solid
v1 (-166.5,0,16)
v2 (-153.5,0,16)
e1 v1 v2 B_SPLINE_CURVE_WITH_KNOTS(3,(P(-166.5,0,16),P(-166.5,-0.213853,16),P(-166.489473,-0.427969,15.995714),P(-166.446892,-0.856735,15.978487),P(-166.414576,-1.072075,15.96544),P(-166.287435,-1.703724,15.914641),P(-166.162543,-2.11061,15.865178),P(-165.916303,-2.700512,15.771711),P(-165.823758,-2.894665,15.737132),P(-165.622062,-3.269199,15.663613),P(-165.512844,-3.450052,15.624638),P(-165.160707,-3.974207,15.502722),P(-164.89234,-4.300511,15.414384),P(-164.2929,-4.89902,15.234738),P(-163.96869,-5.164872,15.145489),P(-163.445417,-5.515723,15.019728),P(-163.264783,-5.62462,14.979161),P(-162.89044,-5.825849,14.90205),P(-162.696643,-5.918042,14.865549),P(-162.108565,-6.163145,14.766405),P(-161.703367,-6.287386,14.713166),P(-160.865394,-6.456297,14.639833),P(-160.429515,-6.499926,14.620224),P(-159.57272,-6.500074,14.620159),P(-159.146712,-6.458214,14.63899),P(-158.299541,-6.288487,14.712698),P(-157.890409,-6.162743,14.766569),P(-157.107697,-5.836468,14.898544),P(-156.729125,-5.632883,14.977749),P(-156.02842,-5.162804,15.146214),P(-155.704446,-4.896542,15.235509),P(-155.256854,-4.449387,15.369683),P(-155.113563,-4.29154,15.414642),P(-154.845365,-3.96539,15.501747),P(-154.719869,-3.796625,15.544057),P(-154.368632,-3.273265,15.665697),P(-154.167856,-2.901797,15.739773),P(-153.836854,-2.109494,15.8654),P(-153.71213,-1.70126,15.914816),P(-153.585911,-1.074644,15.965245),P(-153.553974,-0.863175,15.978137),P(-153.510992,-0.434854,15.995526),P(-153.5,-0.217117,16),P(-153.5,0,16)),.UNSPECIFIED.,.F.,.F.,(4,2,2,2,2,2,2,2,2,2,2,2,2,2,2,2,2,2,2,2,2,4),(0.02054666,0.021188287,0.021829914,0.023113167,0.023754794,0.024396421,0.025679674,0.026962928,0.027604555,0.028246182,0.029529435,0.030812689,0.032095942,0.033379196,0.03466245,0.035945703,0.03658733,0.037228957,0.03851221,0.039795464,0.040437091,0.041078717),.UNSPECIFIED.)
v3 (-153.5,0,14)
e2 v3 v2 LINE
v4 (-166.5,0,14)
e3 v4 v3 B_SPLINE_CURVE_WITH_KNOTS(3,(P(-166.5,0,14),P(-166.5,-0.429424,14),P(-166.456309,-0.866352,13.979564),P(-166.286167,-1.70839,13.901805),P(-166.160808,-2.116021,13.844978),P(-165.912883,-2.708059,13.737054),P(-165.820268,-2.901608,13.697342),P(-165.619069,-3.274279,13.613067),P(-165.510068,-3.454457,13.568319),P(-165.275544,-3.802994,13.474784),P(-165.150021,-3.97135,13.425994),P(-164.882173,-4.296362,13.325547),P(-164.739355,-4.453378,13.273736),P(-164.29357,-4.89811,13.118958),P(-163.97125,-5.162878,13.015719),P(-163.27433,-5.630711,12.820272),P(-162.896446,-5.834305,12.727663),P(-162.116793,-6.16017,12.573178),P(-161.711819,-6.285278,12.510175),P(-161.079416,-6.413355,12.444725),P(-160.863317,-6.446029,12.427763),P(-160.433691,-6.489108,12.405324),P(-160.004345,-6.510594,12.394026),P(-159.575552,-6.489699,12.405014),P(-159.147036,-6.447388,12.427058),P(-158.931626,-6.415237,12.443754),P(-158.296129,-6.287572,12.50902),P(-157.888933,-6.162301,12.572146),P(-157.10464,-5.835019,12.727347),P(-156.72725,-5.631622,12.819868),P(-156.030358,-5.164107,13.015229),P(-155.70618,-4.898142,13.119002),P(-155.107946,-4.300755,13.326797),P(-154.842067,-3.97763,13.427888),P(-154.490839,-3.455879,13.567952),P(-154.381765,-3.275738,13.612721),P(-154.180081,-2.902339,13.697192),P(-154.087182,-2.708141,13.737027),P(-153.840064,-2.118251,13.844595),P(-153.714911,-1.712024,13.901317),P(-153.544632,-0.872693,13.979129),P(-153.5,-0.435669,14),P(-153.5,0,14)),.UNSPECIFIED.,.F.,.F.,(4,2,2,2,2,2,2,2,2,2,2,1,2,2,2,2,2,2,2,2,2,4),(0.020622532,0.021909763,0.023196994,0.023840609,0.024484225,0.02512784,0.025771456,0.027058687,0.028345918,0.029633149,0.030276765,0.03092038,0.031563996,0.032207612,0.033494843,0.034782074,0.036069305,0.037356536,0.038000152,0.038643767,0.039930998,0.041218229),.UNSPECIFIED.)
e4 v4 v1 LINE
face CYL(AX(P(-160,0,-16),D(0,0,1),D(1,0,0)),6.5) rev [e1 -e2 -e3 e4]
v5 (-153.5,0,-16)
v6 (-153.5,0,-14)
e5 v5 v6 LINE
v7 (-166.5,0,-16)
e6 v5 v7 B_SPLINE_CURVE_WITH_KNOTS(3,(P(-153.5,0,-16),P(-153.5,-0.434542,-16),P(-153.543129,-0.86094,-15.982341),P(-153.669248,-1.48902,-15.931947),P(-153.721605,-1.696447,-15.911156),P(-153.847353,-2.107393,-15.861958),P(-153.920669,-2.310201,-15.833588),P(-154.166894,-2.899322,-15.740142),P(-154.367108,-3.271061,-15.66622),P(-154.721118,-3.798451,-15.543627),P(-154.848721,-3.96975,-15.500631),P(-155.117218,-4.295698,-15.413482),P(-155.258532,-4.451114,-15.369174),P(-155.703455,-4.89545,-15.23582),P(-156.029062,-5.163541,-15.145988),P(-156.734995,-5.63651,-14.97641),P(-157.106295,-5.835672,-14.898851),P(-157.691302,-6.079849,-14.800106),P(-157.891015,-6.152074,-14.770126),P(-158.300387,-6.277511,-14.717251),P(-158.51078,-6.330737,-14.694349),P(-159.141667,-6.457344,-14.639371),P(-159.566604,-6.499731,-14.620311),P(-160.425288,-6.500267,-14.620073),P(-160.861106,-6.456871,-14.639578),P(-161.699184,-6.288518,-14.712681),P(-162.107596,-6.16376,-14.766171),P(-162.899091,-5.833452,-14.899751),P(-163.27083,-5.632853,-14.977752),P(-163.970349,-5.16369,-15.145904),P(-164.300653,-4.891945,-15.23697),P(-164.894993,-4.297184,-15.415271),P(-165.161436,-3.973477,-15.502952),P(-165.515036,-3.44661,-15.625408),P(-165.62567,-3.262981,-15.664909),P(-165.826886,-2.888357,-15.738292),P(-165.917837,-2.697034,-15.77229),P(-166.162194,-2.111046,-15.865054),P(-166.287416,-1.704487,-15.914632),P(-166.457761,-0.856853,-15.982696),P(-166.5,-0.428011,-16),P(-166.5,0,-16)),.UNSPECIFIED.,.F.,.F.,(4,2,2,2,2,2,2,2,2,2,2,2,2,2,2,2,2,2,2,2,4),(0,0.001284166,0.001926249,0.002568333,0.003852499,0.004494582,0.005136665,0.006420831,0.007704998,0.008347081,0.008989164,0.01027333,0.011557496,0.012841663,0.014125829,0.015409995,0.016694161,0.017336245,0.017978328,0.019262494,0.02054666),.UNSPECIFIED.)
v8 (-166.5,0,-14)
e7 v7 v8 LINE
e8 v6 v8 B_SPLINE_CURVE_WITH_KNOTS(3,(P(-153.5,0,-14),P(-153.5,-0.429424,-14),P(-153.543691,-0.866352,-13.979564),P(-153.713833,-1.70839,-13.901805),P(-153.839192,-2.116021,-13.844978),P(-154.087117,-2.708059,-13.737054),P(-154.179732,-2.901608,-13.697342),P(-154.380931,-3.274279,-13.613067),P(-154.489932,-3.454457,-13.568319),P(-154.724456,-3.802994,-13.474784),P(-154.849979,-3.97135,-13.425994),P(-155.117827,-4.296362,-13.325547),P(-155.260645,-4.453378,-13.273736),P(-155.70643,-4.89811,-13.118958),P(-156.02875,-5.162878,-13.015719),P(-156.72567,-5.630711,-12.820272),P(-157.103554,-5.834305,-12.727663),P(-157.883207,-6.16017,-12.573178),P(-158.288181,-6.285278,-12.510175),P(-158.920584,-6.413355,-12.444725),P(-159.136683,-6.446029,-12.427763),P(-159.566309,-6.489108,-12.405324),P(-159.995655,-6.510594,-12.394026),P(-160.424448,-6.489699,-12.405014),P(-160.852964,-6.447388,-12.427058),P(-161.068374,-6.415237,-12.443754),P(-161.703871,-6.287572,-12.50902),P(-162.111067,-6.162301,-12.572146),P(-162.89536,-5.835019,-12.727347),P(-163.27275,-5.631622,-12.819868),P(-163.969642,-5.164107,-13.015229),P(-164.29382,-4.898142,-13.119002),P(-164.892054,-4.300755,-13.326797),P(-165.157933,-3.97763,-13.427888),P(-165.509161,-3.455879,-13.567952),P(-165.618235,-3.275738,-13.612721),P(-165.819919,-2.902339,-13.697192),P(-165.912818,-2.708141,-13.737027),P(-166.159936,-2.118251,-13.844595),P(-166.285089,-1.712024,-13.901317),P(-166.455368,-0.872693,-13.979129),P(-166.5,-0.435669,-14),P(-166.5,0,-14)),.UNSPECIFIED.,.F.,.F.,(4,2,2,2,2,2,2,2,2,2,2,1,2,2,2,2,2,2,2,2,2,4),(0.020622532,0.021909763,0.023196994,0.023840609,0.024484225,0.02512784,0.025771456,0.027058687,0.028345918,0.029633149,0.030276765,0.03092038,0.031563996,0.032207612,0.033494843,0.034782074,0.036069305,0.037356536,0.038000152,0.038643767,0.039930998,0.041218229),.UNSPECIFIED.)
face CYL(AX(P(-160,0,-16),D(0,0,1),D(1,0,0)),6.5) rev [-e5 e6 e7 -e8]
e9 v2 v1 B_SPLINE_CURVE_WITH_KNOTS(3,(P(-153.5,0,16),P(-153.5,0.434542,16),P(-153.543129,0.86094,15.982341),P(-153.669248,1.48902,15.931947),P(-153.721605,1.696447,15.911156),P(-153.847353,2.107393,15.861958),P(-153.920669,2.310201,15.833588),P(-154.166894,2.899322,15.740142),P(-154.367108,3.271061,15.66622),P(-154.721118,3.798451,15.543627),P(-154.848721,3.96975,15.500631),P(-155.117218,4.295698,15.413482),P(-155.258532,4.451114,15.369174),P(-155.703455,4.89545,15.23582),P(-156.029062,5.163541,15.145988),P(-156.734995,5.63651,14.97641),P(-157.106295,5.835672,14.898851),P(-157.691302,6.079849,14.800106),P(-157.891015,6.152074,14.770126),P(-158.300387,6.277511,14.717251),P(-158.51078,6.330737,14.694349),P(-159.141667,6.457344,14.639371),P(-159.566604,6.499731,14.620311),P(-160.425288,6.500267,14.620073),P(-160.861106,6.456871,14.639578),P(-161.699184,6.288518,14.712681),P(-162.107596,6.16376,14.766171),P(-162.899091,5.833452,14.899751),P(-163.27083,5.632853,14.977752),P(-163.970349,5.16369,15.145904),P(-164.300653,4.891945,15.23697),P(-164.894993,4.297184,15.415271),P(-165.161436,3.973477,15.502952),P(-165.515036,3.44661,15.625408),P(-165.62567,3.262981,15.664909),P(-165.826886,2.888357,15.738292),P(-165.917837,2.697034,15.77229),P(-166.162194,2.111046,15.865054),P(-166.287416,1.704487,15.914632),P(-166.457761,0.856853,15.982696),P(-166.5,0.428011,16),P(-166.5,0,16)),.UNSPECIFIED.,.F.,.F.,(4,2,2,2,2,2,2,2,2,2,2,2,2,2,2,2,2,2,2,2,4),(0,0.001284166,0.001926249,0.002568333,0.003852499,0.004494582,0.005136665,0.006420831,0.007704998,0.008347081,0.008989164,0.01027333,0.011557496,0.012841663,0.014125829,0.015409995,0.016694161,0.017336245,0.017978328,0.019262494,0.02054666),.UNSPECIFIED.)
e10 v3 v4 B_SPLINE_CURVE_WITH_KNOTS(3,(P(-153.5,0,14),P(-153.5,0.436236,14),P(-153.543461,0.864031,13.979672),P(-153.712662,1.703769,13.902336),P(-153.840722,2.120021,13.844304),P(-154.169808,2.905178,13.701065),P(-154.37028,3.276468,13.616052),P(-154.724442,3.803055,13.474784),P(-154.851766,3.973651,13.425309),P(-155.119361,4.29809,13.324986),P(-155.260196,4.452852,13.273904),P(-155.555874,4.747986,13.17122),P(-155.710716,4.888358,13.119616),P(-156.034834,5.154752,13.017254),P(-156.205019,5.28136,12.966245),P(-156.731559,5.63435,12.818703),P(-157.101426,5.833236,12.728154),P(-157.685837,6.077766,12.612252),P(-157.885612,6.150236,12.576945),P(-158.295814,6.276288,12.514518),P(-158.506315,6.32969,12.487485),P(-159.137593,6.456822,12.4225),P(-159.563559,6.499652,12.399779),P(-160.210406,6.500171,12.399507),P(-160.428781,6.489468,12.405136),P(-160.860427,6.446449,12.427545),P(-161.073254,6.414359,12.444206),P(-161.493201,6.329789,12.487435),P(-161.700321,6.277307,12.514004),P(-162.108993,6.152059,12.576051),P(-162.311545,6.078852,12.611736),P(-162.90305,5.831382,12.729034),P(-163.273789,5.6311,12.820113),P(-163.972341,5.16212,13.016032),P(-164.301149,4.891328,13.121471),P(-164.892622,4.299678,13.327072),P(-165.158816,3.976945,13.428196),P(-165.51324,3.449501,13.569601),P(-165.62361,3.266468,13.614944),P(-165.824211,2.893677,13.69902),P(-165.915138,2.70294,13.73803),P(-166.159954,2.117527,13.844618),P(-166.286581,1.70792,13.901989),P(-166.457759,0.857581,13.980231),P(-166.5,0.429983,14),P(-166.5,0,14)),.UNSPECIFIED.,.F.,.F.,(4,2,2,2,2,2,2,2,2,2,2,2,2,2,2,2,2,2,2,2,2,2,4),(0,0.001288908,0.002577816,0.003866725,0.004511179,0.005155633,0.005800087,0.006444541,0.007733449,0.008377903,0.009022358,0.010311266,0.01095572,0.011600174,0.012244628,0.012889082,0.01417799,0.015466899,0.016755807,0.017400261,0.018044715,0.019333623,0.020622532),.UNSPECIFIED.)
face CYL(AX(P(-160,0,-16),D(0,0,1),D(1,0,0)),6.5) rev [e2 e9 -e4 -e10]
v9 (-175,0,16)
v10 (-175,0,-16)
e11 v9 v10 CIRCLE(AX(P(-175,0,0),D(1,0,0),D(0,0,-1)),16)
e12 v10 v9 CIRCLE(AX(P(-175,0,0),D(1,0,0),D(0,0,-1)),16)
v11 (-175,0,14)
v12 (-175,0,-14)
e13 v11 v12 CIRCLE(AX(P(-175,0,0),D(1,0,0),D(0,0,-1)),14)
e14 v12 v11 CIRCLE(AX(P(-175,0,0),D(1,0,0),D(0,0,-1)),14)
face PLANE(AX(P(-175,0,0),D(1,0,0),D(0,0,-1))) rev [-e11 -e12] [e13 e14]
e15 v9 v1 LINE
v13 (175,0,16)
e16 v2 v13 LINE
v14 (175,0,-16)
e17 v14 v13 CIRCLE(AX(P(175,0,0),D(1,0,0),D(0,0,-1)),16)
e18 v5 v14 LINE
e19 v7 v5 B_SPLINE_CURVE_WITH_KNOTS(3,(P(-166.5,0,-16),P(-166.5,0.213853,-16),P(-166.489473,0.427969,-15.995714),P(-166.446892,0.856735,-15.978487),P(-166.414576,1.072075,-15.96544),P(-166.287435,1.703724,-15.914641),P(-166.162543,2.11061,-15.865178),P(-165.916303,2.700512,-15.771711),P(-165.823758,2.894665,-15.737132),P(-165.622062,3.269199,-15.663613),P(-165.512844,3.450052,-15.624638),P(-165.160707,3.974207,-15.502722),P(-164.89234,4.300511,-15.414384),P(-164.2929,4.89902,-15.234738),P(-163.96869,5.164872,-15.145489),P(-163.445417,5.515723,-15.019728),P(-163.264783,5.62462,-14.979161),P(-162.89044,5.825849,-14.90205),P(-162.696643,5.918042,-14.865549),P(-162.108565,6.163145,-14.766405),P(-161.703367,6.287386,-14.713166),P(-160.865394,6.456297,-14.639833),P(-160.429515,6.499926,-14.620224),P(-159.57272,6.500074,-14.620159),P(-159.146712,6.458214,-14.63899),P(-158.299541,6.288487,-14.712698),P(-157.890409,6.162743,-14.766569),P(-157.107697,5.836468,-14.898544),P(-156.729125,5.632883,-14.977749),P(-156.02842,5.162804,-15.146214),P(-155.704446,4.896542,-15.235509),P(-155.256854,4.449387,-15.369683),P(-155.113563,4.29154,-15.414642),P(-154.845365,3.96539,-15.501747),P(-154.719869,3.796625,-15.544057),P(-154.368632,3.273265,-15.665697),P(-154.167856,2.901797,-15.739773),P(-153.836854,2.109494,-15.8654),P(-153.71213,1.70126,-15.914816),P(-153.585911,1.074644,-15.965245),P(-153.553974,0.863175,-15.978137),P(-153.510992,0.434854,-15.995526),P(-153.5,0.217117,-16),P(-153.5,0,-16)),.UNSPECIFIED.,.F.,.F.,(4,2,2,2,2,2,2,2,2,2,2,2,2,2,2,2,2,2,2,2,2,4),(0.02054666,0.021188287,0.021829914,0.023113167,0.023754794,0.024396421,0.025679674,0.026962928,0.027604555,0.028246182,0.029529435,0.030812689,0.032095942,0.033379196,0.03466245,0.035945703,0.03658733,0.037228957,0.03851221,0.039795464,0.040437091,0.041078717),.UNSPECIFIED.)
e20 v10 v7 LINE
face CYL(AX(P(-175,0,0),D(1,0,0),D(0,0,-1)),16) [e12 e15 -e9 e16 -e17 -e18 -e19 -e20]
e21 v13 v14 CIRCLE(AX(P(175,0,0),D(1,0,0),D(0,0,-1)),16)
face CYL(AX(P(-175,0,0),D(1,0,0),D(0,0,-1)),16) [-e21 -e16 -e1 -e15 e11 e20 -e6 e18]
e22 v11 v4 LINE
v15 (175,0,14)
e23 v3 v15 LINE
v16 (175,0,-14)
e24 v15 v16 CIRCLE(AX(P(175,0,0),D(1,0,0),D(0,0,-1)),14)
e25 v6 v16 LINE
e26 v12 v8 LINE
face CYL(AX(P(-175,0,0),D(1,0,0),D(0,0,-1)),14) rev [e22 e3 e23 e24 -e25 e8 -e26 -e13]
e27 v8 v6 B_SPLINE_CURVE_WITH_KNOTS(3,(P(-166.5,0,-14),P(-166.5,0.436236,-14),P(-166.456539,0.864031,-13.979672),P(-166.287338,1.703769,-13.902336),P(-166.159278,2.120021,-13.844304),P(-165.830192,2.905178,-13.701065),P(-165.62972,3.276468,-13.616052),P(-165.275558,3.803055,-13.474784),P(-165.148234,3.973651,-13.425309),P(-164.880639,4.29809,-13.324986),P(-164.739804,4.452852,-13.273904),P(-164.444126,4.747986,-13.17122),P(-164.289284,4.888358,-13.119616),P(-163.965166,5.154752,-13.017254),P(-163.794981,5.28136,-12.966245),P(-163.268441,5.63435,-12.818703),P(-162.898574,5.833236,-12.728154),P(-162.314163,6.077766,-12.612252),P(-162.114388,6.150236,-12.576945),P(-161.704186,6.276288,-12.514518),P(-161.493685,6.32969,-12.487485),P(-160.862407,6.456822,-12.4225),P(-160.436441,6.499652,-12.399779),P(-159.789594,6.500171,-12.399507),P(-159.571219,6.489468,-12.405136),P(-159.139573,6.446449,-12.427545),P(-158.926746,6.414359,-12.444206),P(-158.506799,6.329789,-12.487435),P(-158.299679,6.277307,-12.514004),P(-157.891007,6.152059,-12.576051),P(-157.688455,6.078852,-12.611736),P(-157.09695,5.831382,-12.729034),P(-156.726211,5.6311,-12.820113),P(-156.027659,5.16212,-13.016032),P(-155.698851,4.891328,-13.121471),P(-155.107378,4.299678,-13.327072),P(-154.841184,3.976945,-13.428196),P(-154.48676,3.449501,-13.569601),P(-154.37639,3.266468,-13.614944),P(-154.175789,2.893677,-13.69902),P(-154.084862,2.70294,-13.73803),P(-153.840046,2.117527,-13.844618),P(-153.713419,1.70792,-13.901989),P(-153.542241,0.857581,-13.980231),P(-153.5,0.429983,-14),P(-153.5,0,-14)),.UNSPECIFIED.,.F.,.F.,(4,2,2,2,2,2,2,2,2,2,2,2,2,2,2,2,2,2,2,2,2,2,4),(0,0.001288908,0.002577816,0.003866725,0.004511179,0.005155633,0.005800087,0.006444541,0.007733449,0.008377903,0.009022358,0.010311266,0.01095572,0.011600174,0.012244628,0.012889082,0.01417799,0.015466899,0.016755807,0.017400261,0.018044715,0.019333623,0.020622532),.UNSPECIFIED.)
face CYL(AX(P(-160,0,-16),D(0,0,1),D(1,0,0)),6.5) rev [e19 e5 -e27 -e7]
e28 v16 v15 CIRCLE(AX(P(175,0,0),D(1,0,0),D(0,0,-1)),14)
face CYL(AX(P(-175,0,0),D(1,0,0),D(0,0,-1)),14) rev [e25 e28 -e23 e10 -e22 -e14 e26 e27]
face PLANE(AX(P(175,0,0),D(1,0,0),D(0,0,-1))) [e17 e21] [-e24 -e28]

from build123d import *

# Parameters (mm, degrees)
SWEEP_1_PROFILE_R        = 16
SWEEP_1_PROFILE_R_2      = 14
CUT_EXTRUDE_1_DEPTH      = 177.456793578
CUT_EXTRUDE_1_DEPTH_BACK = 177.456793578
SKETCH_26_R              = 6.5


with BuildPart() as part:
    # 扫描-薄件1: sweep along a path in 草图1
    with BuildLine(Plane.XY) as sweep_1_path:
        Line((-175, 0), (175, 0))
    # 扫描-薄件1 profile (on start of the path) → 扫描-薄件1 (sweep)
    with BuildSketch(Plane(origin=(-175, 0, 0), x_dir=(0, 0, 1), z_dir=(1, 0, 0))):
        Circle(SWEEP_1_PROFILE_R)
        Circle(SWEEP_1_PROFILE_R_2, mode=Mode.SUBTRACT)
    sweep(path=sweep_1_path.line)

    # 草图26 → 切除-拉伸1 (cut, two sides: drawn at the far end of the back side and taken through both)
    with BuildSketch(Plane.XY.offset(-CUT_EXTRUDE_1_DEPTH_BACK)):
        with Locations((-160, 0)):
            Circle(SKETCH_26_R)
    extrude(amount=CUT_EXTRUDE_1_DEPTH + CUT_EXTRUDE_1_DEPTH_BACK, mode=Mode.SUBTRACT)


solid = part.part
